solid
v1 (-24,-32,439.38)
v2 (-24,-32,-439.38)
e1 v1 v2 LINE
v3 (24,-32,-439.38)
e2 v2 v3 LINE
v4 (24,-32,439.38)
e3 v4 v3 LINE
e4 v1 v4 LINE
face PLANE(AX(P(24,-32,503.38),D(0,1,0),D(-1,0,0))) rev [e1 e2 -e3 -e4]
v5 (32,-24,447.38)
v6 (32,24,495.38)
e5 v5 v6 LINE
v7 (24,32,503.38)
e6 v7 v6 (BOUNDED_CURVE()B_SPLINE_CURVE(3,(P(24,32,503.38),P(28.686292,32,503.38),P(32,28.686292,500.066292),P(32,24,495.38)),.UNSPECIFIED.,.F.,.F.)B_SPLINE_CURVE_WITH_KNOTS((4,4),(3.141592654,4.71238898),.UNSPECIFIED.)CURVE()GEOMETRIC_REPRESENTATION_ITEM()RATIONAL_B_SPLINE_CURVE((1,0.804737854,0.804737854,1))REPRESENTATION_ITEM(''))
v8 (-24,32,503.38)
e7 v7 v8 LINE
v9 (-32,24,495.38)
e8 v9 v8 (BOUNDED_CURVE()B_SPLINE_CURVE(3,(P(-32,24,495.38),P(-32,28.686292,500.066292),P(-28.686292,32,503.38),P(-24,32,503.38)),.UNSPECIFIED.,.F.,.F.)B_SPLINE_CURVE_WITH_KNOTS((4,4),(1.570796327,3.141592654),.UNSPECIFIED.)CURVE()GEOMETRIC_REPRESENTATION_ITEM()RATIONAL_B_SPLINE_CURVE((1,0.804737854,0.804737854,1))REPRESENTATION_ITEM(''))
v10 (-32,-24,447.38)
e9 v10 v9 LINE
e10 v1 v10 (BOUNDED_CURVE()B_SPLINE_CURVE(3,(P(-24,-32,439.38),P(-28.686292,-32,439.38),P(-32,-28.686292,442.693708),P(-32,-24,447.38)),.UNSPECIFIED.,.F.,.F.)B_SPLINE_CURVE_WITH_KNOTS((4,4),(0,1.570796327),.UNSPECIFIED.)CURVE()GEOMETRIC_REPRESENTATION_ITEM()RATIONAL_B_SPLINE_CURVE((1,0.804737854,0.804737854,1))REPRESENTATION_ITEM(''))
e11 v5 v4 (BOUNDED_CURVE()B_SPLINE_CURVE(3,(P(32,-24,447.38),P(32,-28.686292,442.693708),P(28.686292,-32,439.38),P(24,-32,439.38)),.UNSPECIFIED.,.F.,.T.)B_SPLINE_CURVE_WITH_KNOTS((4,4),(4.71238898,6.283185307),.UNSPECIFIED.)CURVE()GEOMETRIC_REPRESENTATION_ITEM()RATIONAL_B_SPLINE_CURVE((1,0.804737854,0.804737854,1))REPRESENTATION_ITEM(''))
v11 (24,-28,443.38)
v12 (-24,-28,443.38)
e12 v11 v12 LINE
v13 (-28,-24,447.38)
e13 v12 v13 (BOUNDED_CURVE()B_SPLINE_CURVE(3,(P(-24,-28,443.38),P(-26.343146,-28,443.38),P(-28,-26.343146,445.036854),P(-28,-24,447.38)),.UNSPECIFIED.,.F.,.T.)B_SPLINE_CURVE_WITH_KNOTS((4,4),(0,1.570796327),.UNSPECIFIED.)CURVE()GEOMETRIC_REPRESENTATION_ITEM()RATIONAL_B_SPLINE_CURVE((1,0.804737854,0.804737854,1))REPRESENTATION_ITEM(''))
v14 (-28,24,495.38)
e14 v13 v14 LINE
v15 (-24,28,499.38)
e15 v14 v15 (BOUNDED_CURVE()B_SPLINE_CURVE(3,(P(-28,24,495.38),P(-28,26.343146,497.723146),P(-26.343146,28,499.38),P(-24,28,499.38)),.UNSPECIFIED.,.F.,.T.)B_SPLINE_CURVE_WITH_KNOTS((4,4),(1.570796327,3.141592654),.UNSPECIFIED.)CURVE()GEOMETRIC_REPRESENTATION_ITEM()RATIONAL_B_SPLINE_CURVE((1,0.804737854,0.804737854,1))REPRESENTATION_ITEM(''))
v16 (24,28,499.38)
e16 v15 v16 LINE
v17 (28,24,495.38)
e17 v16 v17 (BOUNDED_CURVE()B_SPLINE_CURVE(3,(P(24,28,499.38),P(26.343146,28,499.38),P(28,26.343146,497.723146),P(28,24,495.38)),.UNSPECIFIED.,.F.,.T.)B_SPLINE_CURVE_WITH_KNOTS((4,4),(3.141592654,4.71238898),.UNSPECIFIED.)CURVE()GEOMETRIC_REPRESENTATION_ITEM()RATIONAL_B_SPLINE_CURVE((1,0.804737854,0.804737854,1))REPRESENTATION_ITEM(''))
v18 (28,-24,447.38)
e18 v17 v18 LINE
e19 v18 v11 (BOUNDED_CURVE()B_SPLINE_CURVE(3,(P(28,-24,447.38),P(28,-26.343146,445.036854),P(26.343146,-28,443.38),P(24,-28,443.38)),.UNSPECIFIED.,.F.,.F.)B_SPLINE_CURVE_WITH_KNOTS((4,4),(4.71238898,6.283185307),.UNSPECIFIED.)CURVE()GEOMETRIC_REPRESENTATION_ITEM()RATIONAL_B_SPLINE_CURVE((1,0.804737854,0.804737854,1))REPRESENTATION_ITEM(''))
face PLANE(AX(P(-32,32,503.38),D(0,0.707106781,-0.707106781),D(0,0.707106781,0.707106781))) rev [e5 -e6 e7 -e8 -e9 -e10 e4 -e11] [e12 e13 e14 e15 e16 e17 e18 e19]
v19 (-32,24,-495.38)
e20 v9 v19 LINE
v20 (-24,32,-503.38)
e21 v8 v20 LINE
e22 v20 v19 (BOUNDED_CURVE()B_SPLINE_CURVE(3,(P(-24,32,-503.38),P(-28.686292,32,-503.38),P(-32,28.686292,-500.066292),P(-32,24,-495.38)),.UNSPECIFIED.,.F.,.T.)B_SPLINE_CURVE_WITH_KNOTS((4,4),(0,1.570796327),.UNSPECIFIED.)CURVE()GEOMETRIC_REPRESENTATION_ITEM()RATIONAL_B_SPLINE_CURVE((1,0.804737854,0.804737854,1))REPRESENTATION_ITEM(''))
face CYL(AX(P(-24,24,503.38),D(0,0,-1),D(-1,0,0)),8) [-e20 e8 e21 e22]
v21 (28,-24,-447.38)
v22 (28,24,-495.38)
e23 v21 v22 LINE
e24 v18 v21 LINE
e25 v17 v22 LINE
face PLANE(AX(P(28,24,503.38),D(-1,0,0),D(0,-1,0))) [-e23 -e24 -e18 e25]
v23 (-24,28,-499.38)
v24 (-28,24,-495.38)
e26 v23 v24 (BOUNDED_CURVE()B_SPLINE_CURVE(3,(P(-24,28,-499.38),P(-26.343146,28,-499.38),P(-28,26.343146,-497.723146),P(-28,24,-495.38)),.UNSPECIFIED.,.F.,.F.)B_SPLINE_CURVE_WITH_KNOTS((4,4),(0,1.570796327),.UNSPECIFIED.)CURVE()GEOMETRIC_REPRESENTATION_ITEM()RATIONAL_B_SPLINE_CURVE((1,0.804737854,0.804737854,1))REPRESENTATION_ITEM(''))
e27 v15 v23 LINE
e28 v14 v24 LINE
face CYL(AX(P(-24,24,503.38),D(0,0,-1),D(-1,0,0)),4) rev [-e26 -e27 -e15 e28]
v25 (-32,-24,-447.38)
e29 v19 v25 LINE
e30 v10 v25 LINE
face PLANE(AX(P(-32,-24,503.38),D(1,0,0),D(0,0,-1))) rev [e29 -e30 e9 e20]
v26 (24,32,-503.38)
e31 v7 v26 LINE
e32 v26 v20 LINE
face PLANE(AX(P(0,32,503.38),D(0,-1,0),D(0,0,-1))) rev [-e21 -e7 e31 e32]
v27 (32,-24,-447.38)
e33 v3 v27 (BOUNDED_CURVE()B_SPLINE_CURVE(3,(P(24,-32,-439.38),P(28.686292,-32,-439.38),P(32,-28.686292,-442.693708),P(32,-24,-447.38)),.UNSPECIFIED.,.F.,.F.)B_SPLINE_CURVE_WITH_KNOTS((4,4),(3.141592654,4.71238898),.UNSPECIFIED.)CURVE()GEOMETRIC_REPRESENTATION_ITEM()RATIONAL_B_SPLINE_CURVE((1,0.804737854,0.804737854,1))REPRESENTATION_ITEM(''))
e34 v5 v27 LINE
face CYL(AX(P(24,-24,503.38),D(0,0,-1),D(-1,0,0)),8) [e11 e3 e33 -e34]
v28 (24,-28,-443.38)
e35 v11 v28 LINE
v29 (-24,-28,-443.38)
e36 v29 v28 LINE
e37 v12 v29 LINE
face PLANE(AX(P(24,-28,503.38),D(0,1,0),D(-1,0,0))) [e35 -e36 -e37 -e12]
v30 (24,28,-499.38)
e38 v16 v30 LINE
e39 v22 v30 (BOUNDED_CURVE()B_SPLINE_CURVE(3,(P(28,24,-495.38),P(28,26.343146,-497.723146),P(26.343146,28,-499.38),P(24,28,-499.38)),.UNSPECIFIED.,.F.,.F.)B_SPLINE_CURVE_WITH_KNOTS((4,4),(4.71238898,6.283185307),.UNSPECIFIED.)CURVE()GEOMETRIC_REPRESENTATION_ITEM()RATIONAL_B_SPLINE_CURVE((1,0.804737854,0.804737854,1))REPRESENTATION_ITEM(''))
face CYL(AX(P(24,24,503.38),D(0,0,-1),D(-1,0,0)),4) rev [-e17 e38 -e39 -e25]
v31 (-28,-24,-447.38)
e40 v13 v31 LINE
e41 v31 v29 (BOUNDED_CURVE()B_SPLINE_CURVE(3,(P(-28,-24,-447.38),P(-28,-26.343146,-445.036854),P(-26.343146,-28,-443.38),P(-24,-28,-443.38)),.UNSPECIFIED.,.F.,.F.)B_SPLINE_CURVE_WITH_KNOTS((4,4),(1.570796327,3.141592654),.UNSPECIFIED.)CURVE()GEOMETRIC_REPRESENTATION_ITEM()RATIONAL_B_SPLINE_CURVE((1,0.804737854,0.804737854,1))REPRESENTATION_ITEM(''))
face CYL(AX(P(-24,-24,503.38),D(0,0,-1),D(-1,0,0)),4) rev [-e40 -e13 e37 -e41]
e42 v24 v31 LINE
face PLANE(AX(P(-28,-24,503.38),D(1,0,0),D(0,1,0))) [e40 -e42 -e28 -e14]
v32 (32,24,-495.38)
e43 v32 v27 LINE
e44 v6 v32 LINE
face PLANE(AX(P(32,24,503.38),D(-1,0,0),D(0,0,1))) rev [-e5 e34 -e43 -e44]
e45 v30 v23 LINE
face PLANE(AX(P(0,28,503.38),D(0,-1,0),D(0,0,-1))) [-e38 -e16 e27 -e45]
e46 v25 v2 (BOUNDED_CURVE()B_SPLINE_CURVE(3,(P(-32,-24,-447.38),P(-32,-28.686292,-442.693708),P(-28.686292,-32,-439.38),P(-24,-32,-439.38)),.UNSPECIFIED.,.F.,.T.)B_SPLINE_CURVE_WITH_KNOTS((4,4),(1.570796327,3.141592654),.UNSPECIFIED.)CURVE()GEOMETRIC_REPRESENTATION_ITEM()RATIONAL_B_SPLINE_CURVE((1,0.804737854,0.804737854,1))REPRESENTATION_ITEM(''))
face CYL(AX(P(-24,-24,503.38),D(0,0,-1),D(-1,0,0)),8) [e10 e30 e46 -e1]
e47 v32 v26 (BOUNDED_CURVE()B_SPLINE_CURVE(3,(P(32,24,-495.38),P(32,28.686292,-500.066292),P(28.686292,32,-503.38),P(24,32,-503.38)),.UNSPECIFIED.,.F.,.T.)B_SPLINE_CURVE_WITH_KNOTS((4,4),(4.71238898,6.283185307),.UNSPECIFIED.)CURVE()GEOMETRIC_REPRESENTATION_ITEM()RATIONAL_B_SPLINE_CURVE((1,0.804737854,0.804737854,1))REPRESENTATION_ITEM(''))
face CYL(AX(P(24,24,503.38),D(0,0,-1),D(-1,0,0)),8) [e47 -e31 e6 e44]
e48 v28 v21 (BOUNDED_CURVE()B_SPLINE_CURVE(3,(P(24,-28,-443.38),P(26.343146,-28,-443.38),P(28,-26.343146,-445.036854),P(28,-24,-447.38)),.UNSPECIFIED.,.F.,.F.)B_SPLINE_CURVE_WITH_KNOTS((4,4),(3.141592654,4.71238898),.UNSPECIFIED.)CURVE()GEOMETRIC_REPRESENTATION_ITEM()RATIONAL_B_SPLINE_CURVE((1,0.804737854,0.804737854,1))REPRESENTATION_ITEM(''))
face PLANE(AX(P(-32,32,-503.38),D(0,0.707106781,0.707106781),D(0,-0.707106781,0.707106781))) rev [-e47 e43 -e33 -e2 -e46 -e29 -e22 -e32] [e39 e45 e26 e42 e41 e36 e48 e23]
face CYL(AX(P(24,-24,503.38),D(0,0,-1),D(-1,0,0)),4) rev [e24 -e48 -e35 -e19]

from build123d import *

# Parameters (mm, degrees)
BOSS_EXTRUDE_1_DEPTH     = 503.38
CUT_EXTRUDE_1_DEPTH      = 506.410154627
CUT_EXTRUDE_1_DEPTH_BACK = 506.410154627


with BuildPart() as part:
    # Sketch 1 → Boss-Extrude 1 (new, symmetric)
    with BuildSketch(Plane.XY):
        with BuildLine():
            Line((0, 32), (-24, 32))
            ThreePointArc((-24, 32), (-29.656854249, 29.656854249), (-32, 24))
            Line((-32, 24), (-32, 0))
            Line((-32, 0), (-32, -24))
            ThreePointArc((-32, -24), (-29.656854249, -29.656854249), (-24, -32))
            Line((-24, -32), (24, -32))
            ThreePointArc((24, -32), (29.656854249, -29.656854249), (32, -24))
            Line((32, -24), (32, 0))
            Line((32, 0), (32, 24))
            ThreePointArc((32, 24), (29.656854249, 29.656854249), (24, 32))
            Line((24, 32), (0, 32))
        make_face()
        with BuildLine():
            Line((0, 28), (-24, 28))
            ThreePointArc((-24, 28), (-26.828427125, 26.828427125), (-28, 24))
            Line((-28, 24), (-28, 0))
            Line((-28, 0), (-28, -24))
            ThreePointArc((-28, -24), (-26.828427125, -26.828427125), (-24, -28))
            Line((-24, -28), (24, -28))
            ThreePointArc((24, -28), (26.828427125, -26.828427125), (28, -24))
            Line((28, -24), (28, 0))
            Line((28, 0), (28, 24))
            ThreePointArc((28, 24), (26.828427125, 26.828427125), (24, 28))
            Line((24, 28), (0, 28))
        make_face(mode=Mode.SUBTRACT)
    extrude(amount=BOSS_EXTRUDE_1_DEPTH, both=True)

    # Sketch 2 → Cut-Extrude 1 (cut, two sides: drawn at the far end of the back side and taken through both)
    with BuildSketch(Plane(origin=(0, 0, 0), x_dir=(0, 0, -1), z_dir=(1, 0, 0)).offset(-CUT_EXTRUDE_1_DEPTH_BACK)):
        Polygon((-503.38, 32), (-439.38, -32), (-503.38, -32), align=None)
        Polygon((503.38, -32), (503.38, 32), (439.38, -32), align=None)
    extrude(amount=CUT_EXTRUDE_1_DEPTH + CUT_EXTRUDE_1_DEPTH_BACK, mode=Mode.SUBTRACT)


solid = part.part
